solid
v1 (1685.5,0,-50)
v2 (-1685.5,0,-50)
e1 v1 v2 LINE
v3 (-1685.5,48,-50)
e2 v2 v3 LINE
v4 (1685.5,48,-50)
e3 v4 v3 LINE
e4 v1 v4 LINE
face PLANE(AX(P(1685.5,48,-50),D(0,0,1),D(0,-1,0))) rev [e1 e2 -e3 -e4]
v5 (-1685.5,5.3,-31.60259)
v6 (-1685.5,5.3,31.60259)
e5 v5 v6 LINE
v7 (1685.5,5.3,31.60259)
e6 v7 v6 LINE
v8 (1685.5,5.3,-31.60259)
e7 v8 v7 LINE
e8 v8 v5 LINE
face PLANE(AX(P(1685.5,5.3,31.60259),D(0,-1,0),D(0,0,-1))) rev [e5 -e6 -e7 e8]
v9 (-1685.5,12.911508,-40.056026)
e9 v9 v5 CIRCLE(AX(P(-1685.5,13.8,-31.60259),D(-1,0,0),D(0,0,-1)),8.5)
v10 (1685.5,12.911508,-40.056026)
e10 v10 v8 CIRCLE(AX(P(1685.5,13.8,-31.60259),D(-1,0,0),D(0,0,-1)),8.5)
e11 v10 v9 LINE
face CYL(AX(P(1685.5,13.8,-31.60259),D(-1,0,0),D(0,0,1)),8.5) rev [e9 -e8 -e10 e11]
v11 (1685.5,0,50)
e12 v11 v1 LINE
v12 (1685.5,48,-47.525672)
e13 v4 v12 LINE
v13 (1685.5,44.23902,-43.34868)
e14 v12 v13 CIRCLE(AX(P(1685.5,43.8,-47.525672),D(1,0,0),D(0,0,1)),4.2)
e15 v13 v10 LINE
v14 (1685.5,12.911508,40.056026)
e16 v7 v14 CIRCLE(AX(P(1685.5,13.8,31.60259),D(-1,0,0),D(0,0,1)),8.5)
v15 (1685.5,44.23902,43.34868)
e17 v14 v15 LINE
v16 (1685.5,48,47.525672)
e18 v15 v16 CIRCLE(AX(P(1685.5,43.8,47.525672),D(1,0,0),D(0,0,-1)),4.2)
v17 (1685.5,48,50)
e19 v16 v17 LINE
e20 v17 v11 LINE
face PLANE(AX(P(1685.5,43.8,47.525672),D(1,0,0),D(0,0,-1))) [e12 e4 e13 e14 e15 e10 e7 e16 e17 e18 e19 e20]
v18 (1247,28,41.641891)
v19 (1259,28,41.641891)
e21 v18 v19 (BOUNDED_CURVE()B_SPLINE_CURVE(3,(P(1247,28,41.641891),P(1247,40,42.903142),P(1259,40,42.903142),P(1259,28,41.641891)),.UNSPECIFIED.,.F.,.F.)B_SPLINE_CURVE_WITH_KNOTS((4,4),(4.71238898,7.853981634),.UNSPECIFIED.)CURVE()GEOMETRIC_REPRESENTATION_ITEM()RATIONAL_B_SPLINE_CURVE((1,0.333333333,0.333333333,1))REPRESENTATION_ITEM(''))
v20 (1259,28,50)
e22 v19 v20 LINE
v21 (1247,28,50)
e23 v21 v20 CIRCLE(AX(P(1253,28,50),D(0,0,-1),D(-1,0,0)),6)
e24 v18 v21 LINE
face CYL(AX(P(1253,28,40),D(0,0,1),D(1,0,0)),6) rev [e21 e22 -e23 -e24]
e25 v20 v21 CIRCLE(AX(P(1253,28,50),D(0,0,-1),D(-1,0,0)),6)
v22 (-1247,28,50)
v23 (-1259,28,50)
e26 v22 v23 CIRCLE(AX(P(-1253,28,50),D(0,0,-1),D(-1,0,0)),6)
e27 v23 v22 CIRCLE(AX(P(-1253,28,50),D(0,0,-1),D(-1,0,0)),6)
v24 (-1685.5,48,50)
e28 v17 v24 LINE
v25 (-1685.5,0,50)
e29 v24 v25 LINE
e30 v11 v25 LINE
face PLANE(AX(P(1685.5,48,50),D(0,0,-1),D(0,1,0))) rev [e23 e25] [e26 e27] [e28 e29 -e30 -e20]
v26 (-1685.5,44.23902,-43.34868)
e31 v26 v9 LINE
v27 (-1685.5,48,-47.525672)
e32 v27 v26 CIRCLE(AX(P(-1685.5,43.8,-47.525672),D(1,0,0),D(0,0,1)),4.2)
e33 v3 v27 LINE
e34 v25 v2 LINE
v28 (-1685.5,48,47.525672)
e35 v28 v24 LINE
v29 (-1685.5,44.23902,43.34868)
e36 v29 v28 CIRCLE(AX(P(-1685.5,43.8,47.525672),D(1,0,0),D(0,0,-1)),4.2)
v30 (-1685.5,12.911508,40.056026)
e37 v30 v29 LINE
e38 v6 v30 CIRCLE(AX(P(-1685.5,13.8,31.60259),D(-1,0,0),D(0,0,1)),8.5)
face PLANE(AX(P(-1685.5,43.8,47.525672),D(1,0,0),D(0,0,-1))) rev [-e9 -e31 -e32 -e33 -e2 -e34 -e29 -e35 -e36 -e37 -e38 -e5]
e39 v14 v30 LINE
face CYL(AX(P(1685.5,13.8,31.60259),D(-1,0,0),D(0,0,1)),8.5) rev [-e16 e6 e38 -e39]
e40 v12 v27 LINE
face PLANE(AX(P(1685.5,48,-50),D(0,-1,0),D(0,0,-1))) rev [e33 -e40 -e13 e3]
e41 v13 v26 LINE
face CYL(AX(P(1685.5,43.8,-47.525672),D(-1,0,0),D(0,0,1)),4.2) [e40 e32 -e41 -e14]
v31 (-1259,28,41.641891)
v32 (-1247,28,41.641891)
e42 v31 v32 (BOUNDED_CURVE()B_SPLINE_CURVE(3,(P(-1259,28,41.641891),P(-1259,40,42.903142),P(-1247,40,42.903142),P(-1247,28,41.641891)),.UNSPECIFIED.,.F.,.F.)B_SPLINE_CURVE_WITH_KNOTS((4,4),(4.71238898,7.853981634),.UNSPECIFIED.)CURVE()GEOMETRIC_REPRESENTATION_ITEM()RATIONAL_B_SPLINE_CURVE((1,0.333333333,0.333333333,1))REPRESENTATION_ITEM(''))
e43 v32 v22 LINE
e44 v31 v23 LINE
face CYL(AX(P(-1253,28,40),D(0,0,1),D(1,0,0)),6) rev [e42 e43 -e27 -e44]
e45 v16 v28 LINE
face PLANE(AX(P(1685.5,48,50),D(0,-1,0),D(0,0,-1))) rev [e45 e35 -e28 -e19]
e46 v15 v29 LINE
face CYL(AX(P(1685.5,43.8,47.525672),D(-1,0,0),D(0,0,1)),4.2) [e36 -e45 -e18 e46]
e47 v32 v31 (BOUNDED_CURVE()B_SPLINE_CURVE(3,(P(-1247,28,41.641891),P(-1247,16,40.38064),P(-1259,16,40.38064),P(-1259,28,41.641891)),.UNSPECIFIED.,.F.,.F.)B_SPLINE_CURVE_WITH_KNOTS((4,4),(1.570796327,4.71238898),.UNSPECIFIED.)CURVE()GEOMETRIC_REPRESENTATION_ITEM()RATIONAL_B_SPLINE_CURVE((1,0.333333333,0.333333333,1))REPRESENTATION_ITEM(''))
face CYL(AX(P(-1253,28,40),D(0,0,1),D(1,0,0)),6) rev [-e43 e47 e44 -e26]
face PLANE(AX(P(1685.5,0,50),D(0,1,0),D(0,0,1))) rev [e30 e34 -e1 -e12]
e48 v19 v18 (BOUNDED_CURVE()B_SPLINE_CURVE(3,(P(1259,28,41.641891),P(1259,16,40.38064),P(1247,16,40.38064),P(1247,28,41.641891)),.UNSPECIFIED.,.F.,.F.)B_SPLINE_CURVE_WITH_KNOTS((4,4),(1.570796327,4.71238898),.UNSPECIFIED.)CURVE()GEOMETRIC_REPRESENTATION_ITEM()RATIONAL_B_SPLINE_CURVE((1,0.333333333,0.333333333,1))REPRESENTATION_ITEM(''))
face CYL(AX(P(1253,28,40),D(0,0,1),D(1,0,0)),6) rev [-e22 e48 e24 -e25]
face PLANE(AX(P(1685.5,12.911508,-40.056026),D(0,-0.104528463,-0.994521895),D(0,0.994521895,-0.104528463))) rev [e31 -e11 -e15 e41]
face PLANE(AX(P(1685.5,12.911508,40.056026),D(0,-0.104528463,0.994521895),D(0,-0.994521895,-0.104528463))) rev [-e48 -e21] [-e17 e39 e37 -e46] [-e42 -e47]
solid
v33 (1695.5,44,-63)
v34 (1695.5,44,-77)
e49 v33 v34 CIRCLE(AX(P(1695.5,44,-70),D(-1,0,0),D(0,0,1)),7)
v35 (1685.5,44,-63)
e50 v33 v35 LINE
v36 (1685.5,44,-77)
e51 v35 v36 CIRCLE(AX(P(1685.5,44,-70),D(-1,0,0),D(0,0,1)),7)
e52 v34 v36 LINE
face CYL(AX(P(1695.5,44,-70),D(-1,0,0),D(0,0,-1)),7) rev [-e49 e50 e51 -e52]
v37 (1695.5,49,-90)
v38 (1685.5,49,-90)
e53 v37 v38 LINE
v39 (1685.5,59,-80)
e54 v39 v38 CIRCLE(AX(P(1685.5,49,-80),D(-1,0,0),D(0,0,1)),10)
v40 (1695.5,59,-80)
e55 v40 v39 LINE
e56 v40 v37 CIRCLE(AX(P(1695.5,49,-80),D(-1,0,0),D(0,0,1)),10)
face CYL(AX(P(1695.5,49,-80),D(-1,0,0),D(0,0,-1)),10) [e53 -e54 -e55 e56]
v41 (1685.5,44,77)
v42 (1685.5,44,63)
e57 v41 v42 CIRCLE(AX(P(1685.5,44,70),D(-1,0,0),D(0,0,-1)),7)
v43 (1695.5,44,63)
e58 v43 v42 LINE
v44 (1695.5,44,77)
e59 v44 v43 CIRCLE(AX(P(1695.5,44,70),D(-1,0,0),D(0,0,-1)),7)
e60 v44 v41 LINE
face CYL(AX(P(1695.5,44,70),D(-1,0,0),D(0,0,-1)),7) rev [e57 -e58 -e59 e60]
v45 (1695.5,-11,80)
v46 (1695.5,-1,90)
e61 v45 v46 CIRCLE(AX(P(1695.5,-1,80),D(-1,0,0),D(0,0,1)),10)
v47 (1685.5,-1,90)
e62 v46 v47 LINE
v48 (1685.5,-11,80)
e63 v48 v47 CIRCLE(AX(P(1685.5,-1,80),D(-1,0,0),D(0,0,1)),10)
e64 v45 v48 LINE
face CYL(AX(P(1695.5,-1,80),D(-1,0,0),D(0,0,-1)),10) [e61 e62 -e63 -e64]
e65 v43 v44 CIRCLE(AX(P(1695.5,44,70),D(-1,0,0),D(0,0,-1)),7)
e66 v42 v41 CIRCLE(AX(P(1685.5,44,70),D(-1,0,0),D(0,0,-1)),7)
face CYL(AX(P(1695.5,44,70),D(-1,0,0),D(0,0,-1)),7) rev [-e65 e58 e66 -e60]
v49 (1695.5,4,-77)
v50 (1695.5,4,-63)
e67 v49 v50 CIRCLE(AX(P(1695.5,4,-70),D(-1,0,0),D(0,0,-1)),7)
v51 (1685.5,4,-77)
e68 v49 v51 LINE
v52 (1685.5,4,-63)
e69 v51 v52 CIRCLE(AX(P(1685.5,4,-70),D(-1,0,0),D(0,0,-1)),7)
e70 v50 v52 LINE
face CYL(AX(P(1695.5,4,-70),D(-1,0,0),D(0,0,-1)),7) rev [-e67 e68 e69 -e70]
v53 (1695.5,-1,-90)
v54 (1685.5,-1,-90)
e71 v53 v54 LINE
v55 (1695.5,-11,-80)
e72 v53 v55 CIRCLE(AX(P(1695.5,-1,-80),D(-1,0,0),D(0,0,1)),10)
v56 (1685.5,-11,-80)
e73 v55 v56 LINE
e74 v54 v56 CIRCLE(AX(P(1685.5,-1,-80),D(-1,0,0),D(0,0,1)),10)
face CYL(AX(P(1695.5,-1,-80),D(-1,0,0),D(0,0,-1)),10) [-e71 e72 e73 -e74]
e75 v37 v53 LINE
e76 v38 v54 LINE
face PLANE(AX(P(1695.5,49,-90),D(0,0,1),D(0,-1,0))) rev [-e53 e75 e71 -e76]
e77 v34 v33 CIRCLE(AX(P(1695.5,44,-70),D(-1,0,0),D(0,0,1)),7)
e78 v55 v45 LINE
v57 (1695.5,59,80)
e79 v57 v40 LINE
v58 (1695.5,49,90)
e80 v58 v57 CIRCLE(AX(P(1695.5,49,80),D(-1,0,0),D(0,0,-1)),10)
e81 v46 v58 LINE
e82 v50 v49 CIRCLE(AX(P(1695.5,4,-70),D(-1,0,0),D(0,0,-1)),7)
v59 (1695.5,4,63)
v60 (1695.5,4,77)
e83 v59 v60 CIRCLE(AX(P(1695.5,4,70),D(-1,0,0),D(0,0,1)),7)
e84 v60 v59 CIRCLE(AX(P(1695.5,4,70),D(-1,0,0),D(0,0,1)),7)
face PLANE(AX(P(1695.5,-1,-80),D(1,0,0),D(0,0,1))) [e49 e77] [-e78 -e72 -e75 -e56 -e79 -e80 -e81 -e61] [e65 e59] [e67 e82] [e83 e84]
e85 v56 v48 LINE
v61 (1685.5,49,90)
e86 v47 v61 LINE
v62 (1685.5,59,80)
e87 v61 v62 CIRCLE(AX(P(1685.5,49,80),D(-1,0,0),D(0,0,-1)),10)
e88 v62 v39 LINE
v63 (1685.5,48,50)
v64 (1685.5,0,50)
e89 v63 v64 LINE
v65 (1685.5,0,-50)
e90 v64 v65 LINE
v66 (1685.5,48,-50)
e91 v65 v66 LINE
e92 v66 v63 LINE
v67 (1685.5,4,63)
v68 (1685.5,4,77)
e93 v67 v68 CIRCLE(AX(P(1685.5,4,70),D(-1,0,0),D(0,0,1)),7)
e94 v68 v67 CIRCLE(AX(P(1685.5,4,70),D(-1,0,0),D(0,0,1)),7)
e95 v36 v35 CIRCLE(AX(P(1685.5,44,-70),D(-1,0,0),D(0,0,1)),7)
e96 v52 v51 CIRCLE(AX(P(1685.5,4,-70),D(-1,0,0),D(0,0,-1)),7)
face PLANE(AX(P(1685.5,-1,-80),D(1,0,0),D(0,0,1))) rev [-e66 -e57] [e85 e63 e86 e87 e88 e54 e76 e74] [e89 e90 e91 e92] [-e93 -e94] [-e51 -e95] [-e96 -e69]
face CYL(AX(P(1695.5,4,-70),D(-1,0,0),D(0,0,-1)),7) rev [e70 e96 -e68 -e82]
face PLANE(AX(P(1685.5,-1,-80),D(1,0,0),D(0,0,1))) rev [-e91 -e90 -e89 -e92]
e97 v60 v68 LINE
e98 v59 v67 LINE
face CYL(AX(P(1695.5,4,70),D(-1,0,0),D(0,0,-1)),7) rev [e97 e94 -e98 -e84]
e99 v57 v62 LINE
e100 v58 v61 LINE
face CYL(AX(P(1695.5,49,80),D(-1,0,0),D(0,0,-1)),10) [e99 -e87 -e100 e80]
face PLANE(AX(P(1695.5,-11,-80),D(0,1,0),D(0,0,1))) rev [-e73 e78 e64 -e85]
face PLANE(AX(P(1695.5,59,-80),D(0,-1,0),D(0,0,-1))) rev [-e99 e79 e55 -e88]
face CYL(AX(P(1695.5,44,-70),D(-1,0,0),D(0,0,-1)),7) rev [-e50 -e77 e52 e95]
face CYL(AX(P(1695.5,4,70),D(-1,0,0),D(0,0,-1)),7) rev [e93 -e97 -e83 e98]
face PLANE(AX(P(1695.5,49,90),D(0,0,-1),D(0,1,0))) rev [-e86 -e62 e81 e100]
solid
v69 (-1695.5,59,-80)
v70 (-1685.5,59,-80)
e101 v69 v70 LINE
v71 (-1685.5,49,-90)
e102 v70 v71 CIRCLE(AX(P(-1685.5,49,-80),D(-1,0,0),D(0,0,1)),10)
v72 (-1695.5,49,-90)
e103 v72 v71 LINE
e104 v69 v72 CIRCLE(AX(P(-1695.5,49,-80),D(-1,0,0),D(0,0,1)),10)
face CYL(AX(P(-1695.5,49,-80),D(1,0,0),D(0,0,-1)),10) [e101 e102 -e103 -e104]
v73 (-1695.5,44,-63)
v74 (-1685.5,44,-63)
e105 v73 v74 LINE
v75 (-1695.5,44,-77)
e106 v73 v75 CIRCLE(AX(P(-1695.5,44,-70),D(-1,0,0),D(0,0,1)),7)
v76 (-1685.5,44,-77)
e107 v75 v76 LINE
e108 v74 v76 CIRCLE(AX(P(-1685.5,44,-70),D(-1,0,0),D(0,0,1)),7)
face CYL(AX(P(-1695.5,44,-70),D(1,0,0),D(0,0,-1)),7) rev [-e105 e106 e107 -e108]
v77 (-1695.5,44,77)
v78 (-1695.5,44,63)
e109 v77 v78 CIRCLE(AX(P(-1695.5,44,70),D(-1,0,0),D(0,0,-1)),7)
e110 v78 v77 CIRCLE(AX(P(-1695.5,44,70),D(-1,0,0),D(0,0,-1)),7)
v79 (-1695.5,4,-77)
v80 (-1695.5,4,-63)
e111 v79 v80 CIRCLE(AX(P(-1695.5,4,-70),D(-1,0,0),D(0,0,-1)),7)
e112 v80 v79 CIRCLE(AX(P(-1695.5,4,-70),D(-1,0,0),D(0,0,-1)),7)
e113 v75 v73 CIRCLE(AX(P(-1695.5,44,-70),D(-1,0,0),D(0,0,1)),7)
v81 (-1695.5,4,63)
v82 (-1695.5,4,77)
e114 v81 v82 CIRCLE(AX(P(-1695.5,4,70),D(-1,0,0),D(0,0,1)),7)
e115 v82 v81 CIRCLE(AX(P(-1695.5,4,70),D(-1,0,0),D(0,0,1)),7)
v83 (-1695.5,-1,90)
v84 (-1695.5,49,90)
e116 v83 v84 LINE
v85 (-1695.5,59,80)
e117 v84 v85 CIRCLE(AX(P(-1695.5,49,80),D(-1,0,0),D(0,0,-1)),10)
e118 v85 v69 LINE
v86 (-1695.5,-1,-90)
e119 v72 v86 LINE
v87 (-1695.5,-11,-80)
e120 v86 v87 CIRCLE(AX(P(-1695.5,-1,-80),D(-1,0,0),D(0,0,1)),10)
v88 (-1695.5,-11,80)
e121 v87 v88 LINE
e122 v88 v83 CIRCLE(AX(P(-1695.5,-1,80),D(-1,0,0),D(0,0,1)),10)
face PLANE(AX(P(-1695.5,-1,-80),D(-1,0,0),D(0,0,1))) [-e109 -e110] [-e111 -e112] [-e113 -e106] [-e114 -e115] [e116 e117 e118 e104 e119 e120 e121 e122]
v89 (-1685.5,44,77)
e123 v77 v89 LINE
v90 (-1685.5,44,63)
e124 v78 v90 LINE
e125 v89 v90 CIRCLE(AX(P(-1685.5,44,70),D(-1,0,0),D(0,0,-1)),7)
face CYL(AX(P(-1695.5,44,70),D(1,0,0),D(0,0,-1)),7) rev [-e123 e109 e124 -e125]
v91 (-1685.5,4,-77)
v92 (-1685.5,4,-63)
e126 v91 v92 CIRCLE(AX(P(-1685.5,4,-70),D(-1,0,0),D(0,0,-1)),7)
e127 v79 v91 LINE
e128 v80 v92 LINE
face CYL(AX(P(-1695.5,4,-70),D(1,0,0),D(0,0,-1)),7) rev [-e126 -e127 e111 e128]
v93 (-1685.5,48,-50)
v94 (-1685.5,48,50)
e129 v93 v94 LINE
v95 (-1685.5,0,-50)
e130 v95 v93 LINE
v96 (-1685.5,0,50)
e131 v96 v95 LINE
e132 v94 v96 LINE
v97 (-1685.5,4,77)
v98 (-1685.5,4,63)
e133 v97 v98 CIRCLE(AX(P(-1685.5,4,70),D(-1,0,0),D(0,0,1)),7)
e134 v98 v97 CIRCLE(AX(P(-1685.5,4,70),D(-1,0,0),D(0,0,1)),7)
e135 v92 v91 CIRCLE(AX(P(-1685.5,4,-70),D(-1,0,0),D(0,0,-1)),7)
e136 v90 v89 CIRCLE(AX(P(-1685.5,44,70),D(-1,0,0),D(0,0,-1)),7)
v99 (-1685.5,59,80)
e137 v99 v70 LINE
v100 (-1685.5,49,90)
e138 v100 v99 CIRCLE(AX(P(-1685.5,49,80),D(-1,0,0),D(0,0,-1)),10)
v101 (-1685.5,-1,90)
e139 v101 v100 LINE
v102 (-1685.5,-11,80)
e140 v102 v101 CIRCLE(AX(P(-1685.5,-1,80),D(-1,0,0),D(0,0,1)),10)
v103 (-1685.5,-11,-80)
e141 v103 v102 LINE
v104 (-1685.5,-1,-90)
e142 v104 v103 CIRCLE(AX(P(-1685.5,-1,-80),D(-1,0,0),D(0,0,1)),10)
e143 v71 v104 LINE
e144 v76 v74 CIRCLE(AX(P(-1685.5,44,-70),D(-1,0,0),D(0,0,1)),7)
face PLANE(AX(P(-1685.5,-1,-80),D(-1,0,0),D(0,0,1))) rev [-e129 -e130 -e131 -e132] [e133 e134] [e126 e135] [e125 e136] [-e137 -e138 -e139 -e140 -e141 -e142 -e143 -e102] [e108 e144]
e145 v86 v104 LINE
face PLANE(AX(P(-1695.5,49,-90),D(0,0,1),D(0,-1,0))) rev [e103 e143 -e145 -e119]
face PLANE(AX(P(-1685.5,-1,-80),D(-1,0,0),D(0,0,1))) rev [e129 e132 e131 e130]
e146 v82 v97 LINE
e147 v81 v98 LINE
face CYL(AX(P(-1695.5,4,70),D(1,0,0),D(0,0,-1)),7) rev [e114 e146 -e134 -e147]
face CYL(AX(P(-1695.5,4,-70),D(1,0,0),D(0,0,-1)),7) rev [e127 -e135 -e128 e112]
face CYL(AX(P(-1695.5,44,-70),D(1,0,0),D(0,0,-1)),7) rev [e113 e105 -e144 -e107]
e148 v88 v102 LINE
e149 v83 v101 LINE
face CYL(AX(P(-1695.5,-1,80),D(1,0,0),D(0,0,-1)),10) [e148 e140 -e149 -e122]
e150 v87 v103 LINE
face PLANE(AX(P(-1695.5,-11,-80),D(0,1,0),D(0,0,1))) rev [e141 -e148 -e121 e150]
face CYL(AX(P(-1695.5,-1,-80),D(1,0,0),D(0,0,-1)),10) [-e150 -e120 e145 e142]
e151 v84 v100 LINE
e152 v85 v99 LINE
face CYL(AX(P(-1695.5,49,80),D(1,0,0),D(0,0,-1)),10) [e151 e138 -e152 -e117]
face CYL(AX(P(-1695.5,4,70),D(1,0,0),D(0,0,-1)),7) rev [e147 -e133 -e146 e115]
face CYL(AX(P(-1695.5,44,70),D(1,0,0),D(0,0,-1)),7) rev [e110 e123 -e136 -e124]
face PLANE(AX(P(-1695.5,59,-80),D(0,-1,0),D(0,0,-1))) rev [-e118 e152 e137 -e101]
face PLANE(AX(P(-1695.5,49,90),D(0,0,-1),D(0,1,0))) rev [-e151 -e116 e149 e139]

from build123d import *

# Parameters (mm, degrees)
GB_T707_1988_HOT_ROLLED_CHANNEL_10_1_DEPTH = 3371
SKETCH3_R                                  = 7
BOSS_EXTRUDE1_DEPTH                        = 10
SKETCH9_R                                  = 6
CUT_EXTRUDE1_DEPTH                         = 10


with BuildPart() as part:
    # Sketch13 → Gb／t707-1988 Hot-Rolled Channel 10(1) (new body)
    with BuildSketch(Plane(origin=(-1685.5, 0, -50), x_dir=(0, 1, 0), z_dir=(1, 0, 0))):
        with BuildLine():
            Line((48, 100), (0, 100))
            Line((0, 100), (0, 0))
            Line((0, 0), (48, 0))
            Line((48, 0), (48, 2.474327591))
            ThreePointArc((48, 2.474327591), (46.921208267, 5.284676138), (44.239019546, 6.651319552))
            Line((44.239019546, 6.651319552), (12.911508062, 9.943973689))
            ThreePointArc((12.911508062, 9.943973689), (7.483268983, 12.709799645), (5.3, 18.397409799))
            Line((5.3, 18.397409799), (5.3, 81.602590201))
            ThreePointArc((5.3, 81.602590201), (7.483268983, 87.290200355), (12.911508062, 90.056026311))
            Line((12.911508062, 90.056026311), (44.239019546, 93.348680448))
            ThreePointArc((44.239019546, 93.348680448), (46.921208267, 94.715323862), (48, 97.525672409))
            Line((48, 97.525672409), (48, 100))
        make_face()
    extrude(amount=GB_T707_1988_HOT_ROLLED_CHANNEL_10_1_DEPTH)

    # Sketch9 → Cut-Extrude1 (cut)
    with BuildSketch(Plane(origin=(0, 0, 50), x_dir=(-1, 0, 0), z_dir=(0, 0, -1))):
        with Locations(Location((-1253, 28, 0), (0, 0, 90))):
            Circle(SKETCH9_R)
        with Locations(Location((1253, 28, 0), (0, 0, 90))):
            Circle(SKETCH9_R)
    extrude(amount=CUT_EXTRUDE1_DEPTH, mode=Mode.SUBTRACT)


with BuildPart() as body_2:
    # Sketch3 → Boss-Extrude1 (new body)
    with BuildSketch(Plane.ZY.offset(1685.5)):
        with BuildLine():
            Line((-80, 59), (80, 59))
            ThreePointArc((80, 59), (87.071067812, 56.071067812), (90, 49))
            Line((90, 49), (90, -1))
            ThreePointArc((90, -1), (87.071067812, -8.071067812), (80, -11))
            Line((80, -11), (-80, -11))
            ThreePointArc((-80, -11), (-87.071067812, -8.071067812), (-90, -1))
            Line((-90, -1), (-90, 49))
            ThreePointArc((-90, 49), (-87.071067812, 56.071067812), (-80, 59))
        make_face()
        with Locations((-70, 44)):
            Circle(SKETCH3_R, mode=Mode.SUBTRACT)
        with Locations(Location((-70, 4, 0), (0, 0, 180))):
            Circle(SKETCH3_R, mode=Mode.SUBTRACT)
        with Locations((70, 4)):
            Circle(SKETCH3_R, mode=Mode.SUBTRACT)
        with Locations(Location((70, 44, 0), (0, 0, 180))):
            Circle(SKETCH3_R, mode=Mode.SUBTRACT)
    extrude(amount=BOSS_EXTRUDE1_DEPTH)


with BuildPart() as body_3:
    # Mirror3: mirrored copy
    add(body_2.part.mirror(Plane(origin=(0, 0, 0), x_dir=(0, 0, 1), z_dir=(1, 0, 0))))


solid = Compound([part.part, body_2.part, body_3.part])
